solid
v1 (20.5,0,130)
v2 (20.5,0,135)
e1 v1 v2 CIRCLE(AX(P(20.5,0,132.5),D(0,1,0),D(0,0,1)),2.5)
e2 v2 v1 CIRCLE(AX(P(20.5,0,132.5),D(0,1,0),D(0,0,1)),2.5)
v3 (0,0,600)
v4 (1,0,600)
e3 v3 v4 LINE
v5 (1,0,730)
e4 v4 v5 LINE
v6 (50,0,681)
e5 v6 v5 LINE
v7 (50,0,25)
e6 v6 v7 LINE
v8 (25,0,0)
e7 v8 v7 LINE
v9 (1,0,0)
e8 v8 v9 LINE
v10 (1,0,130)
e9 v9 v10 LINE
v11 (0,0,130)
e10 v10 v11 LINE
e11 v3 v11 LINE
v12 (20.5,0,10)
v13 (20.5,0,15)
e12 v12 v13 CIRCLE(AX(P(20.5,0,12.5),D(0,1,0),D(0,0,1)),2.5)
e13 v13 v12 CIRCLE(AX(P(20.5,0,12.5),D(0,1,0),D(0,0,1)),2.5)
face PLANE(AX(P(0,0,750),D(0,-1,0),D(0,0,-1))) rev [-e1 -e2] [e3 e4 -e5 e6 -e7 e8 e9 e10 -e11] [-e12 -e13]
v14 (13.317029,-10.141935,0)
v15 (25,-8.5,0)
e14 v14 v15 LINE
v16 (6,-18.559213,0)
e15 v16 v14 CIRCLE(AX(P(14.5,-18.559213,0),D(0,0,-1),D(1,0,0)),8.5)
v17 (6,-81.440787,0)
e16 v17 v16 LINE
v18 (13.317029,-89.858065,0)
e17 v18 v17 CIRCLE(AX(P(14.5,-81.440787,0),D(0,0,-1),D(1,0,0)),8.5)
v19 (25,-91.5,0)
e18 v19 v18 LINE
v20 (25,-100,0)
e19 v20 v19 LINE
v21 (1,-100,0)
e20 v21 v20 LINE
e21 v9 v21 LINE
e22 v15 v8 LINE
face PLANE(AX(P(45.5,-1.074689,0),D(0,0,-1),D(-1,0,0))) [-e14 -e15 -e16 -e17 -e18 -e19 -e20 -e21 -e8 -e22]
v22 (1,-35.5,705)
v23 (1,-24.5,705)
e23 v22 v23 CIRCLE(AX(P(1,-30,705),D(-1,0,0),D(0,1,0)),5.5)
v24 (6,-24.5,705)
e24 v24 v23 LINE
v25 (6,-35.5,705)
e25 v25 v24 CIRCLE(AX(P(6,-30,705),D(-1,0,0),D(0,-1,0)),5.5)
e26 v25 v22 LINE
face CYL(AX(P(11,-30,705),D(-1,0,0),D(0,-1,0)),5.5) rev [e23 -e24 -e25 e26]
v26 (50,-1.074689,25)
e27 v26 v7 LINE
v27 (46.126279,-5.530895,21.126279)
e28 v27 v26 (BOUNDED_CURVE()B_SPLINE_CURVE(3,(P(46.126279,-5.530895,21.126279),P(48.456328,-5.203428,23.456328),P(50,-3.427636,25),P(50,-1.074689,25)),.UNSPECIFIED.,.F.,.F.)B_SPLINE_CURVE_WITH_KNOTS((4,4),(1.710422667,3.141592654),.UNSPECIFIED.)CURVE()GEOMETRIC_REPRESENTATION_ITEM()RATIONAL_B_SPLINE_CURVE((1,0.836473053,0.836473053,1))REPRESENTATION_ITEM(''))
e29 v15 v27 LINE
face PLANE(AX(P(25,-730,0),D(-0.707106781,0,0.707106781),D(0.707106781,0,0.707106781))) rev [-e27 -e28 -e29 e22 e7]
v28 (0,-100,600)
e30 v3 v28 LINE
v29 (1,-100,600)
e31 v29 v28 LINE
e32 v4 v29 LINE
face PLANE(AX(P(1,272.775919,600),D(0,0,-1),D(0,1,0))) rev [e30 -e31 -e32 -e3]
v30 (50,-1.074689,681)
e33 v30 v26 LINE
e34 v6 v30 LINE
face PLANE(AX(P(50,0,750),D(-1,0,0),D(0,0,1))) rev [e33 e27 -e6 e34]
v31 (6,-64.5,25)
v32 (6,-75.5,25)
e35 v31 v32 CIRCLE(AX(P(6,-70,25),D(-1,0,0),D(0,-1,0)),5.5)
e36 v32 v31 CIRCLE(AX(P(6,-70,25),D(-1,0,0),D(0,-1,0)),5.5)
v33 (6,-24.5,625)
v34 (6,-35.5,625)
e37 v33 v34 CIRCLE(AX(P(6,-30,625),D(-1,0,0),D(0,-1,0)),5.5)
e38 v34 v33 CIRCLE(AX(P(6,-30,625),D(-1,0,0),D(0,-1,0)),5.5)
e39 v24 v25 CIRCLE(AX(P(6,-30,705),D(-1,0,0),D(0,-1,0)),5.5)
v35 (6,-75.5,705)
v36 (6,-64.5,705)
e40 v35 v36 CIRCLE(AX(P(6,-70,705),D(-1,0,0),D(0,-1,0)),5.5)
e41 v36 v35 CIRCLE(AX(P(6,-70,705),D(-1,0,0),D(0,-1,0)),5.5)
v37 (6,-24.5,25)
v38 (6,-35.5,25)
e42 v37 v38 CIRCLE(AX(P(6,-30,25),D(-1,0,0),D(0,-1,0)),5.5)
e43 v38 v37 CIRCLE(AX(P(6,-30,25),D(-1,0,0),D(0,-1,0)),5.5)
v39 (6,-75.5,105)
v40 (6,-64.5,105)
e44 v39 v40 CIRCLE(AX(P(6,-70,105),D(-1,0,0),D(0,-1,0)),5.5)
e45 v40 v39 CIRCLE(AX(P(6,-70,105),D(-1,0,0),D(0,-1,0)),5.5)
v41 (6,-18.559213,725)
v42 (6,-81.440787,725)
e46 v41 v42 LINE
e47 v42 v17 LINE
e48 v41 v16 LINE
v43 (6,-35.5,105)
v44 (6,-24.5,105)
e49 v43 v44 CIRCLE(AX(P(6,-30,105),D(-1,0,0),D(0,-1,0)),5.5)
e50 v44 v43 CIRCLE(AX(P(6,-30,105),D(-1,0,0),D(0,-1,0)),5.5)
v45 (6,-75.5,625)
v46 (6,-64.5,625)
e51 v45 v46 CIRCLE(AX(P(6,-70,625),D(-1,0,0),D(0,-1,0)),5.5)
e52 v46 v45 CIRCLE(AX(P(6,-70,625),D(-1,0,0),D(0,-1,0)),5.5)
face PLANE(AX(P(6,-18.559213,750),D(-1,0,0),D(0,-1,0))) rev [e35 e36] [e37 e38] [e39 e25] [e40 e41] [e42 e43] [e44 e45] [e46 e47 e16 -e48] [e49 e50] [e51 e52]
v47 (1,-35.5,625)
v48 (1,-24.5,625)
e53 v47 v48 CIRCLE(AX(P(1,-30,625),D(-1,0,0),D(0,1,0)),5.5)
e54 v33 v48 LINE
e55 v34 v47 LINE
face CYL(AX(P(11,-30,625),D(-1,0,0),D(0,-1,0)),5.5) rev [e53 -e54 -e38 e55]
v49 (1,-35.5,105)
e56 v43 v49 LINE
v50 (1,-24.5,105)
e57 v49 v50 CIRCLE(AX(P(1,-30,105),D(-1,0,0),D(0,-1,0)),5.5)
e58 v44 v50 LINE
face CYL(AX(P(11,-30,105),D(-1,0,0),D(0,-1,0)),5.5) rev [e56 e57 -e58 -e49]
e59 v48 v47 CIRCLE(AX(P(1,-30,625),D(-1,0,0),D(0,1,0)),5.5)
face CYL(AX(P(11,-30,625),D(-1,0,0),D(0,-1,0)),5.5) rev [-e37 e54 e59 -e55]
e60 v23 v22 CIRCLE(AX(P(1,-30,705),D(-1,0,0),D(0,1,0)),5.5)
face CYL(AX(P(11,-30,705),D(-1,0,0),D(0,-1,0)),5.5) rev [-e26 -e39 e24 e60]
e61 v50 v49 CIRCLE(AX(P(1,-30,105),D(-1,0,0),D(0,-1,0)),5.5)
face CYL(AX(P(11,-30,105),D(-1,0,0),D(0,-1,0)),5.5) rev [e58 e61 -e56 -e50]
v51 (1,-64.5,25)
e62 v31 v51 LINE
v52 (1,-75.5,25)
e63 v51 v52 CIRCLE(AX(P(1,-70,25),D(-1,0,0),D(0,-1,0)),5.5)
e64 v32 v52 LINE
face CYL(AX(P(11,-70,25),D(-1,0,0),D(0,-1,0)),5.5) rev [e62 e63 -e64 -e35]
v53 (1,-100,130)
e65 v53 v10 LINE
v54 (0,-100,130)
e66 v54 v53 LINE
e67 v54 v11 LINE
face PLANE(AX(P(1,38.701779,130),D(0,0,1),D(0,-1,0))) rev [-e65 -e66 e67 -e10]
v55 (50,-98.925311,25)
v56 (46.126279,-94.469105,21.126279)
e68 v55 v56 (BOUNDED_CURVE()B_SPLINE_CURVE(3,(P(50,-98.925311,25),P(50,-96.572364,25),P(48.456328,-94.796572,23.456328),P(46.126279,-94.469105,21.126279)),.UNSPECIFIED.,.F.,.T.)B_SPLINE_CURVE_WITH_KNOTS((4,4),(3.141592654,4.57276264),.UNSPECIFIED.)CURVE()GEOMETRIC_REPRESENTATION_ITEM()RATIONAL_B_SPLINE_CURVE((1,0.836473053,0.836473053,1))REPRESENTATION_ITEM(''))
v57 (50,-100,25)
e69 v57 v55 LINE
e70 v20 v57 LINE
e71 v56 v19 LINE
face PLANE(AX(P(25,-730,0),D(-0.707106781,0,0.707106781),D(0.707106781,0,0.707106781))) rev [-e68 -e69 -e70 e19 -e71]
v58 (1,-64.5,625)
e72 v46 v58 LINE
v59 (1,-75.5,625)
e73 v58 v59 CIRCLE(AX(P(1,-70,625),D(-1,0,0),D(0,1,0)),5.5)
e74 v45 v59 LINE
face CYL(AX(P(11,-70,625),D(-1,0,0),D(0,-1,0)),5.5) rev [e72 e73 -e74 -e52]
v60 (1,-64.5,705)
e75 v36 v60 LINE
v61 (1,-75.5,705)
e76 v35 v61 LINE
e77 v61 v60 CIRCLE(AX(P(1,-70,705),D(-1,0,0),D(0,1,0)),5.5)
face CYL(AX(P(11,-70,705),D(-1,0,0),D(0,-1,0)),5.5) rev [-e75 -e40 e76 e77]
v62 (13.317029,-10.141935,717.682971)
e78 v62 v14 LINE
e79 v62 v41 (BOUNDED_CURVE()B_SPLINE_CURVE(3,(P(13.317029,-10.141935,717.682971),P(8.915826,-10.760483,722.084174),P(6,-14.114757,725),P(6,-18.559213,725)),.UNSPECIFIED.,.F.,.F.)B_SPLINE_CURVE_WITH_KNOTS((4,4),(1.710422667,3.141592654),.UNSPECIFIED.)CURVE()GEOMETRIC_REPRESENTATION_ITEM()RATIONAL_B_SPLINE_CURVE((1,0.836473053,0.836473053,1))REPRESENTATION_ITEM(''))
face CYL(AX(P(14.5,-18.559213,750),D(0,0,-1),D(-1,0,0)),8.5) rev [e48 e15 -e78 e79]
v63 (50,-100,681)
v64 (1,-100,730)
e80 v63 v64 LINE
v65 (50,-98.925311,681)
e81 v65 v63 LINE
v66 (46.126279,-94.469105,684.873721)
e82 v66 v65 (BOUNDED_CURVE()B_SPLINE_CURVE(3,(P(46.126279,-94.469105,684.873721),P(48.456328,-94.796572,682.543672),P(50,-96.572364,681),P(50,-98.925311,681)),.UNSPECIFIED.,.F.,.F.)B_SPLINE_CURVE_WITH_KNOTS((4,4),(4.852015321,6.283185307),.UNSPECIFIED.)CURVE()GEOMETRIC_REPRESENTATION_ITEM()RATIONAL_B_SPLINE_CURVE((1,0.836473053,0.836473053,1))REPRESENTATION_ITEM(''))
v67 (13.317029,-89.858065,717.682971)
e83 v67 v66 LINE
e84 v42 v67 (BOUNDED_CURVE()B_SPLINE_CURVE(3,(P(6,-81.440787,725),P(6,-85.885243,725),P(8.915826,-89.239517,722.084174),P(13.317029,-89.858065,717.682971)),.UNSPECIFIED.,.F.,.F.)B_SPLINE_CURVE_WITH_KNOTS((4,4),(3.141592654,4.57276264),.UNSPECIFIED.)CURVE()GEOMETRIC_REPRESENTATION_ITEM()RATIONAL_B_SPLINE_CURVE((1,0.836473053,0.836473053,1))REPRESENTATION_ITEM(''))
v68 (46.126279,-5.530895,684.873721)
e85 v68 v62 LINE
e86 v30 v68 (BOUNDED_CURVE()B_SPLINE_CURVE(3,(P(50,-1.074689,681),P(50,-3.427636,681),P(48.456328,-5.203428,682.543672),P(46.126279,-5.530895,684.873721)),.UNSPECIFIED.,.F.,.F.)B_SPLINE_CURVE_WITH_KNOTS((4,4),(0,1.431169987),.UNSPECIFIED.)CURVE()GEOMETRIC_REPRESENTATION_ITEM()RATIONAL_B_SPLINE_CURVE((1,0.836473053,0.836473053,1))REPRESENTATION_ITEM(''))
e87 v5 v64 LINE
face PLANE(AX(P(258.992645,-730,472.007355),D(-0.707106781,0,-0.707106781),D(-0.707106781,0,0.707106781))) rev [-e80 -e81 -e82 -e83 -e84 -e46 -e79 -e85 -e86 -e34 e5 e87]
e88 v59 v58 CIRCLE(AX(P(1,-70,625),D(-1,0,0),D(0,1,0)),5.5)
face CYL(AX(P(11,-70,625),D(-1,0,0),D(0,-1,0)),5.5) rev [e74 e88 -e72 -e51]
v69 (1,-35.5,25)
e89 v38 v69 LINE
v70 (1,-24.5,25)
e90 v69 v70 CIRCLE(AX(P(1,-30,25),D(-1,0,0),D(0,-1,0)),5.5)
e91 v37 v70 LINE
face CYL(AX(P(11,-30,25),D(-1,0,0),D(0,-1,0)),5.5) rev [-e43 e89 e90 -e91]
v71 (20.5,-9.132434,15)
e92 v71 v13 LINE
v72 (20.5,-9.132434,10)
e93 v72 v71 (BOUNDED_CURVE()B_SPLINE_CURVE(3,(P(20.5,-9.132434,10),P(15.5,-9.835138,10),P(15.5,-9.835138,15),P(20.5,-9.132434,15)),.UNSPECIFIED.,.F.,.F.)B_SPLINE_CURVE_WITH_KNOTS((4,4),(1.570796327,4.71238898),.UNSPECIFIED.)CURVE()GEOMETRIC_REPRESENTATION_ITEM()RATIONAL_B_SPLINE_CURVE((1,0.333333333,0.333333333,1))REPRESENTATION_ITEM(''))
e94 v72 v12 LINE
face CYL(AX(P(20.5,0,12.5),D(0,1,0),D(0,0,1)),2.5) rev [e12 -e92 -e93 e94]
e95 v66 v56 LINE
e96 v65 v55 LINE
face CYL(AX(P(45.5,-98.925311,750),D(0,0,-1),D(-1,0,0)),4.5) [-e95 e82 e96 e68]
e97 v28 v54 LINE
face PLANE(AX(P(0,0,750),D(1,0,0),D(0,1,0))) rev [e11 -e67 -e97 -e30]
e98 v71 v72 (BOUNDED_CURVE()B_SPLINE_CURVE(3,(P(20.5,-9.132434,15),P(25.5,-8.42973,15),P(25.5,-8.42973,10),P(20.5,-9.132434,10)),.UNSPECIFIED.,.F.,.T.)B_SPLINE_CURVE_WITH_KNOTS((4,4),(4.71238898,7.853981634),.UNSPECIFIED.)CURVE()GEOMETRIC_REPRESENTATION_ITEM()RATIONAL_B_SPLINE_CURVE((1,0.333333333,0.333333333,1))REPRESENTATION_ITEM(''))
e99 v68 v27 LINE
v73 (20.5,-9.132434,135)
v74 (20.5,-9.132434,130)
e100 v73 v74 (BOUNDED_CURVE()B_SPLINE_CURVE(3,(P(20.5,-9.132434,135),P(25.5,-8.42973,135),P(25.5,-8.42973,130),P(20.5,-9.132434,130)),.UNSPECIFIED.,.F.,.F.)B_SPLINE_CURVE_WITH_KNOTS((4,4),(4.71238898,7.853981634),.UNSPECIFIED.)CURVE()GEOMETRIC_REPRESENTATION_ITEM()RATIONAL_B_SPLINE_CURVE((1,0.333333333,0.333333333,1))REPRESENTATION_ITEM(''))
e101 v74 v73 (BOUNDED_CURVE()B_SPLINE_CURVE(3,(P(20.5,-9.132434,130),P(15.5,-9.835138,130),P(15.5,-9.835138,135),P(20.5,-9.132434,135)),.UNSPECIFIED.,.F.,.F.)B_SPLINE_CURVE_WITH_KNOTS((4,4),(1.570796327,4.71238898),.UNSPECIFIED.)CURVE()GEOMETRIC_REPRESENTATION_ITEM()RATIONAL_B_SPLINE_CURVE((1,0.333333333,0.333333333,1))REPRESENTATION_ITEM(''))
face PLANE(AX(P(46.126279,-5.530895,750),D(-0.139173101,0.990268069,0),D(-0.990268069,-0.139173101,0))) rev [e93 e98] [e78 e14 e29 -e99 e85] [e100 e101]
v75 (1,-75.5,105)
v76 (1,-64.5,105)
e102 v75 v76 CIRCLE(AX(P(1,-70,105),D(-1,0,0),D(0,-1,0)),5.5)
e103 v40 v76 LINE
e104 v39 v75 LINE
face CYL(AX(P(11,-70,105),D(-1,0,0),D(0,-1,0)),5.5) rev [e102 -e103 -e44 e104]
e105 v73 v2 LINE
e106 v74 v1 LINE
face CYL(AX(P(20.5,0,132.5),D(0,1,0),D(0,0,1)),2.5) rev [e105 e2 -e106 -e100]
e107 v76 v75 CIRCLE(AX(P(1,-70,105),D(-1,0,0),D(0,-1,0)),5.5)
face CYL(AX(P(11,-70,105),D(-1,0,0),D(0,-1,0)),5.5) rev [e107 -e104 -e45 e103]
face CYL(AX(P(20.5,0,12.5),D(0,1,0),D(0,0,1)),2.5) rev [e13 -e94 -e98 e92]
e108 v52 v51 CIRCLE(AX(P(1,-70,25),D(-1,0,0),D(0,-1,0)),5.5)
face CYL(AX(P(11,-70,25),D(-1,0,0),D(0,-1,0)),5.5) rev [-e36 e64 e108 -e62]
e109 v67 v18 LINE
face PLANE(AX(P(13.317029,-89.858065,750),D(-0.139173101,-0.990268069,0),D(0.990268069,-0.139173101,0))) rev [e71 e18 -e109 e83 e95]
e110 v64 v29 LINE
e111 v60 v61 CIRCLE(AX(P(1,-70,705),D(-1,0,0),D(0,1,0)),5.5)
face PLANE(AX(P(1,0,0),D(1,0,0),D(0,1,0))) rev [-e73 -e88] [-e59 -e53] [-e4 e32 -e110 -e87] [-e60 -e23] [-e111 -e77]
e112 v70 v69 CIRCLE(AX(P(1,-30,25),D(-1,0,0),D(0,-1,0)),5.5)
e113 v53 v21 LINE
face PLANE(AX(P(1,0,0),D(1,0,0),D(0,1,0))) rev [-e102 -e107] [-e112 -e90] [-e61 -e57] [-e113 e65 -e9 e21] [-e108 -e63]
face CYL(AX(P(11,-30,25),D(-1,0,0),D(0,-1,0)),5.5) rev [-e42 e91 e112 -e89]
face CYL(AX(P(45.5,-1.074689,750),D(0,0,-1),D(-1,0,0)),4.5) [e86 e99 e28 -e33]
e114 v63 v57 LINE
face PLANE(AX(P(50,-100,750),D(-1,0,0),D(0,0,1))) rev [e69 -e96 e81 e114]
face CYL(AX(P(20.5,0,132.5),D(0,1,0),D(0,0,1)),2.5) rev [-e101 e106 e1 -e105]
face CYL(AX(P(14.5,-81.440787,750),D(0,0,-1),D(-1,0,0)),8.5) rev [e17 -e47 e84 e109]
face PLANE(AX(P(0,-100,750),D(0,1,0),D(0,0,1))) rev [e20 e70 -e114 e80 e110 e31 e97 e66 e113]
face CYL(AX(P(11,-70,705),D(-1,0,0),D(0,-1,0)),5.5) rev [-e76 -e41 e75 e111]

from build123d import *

# Parameters (mm, degrees)
BOSS_EXTRUDE1_DEPTH   = 750
CUT_EXTRUDE1_DEPTH    = 730
SKETCH3_W             = 246.792493201
SKETCH3_H             = 411.477698095
CUT_EXTRUDE2_DEPTH    = 1
SKETCH4_R             = 5.5
CUT_EXTRUDE3_DEPTH    = 10
M6_TAPPED_HOLE3_D     = 5
M6_TAPPED_HOLE3_DEPTH = 15
M6_TAPPED_HOLE3_TIP   = 1.502151548


with BuildPart() as part:
    # Sketch1 → Boss-Extrude1 (new body)
    with BuildSketch(Plane.XY):
        with BuildLine():
            Line((0, 0), (0, -100))
            Line((0, -100), (50, -100))
            Line((50, -100), (50, -98.925311188))
            ThreePointArc((50, -98.925311188), (48.896193111, -95.973045557), (46.126278954, -94.469104878))
            Line((46.126278954, -94.469104878), (13.317028642, -89.858065454))
            ThreePointArc((13.317028642, -89.858065454), (8.084968568, -87.017288616), (6, -81.440786869))
            Line((6, -81.440786869), (6, -18.559213131))
            ThreePointArc((6, -18.559213131), (8.084968568, -12.982711384), (13.317028642, -10.141934546))
            Line((13.317028642, -10.141934546), (46.126278954, -5.530895122))
            ThreePointArc((46.126278954, -5.530895122), (48.896193111, -4.026954443), (50, -1.074688812))
            Line((50, -1.074688812), (50, 0))
            Line((50, 0), (0, 0))
        make_face()
    extrude(amount=BOSS_EXTRUDE1_DEPTH)

    # Sketch2 → Cut-Extrude1 (cut)
    with BuildSketch(Plane(origin=(0, 0, 0), x_dir=(1, 0, 0), z_dir=(0, 1, 0))):
        Polygon((258.992644717, -472.007355283), (0, -731), (-59.777153602, -772.262203455), (30.841373369, -818.159898935), (45.044802943, -785.872759949), (459.456990019, -587.675626999), align=None)
        Polygon((25, 0), (50, -25), (50, 48.41721094), align=None)
    extrude(amount=-CUT_EXTRUDE1_DEPTH, mode=Mode.SUBTRACT)

    # Sketch3 → Cut-Extrude2 (cut)
    with BuildSketch(Plane.ZY):
        Polygon((130, 38.70177923), (130, -162.725177772), (-125.633599865, -119.606257313), (-100.418312462, 29.884375145), align=None)
        with Locations((723.396246601, 67.037069817)):
            Rectangle(SKETCH3_W, SKETCH3_H)
    extrude(amount=-CUT_EXTRUDE2_DEPTH, mode=Mode.SUBTRACT)

    # Sketch4 → Cut-Extrude3 (cut)
    with BuildSketch(Plane.ZY.offset(-1)):
        with Locations(Location((25, -30, 0), (0, 0, 270))):
            Circle(SKETCH4_R)
        with Locations(Location((105, -30, 0), (0, 0, 270))):
            Circle(SKETCH4_R)
        with Locations(Location((25, -70, 0), (0, 0, 270))):
            Circle(SKETCH4_R)
        with Locations(Location((105, -70, 0), (0, 0, 270))):
            Circle(SKETCH4_R)
        with Locations(Location((625, -30, 0), (0, 0, 270))):
            Circle(SKETCH4_R)
        with Locations(Location((705, -70, 0), (0, 0, 270))):
            Circle(SKETCH4_R)
        with Locations(Location((625, -70, 0), (0, 0, 270))):
            Circle(SKETCH4_R)
        with Locations(Location((705, -30, 0), (0, 0, 270))):
            Circle(SKETCH4_R)
    extrude(amount=-CUT_EXTRUDE3_DEPTH, mode=Mode.SUBTRACT)

    # M6 Tapped Hole3
    with Locations(Plane(origin=(0, 0, 0), x_dir=(1, 0, 0), z_dir=(0, 1, 0))):
        with Locations((20.5, -12.5), (20.5, -132.5)):
            Hole(M6_TAPPED_HOLE3_D / 2, depth=M6_TAPPED_HOLE3_DEPTH)
            with Locations((0, 0, -(M6_TAPPED_HOLE3_DEPTH + M6_TAPPED_HOLE3_TIP / 2))):  # 118° drill point
                Cone(0, M6_TAPPED_HOLE3_D / 2, M6_TAPPED_HOLE3_TIP, mode=Mode.SUBTRACT)


solid = part.part
